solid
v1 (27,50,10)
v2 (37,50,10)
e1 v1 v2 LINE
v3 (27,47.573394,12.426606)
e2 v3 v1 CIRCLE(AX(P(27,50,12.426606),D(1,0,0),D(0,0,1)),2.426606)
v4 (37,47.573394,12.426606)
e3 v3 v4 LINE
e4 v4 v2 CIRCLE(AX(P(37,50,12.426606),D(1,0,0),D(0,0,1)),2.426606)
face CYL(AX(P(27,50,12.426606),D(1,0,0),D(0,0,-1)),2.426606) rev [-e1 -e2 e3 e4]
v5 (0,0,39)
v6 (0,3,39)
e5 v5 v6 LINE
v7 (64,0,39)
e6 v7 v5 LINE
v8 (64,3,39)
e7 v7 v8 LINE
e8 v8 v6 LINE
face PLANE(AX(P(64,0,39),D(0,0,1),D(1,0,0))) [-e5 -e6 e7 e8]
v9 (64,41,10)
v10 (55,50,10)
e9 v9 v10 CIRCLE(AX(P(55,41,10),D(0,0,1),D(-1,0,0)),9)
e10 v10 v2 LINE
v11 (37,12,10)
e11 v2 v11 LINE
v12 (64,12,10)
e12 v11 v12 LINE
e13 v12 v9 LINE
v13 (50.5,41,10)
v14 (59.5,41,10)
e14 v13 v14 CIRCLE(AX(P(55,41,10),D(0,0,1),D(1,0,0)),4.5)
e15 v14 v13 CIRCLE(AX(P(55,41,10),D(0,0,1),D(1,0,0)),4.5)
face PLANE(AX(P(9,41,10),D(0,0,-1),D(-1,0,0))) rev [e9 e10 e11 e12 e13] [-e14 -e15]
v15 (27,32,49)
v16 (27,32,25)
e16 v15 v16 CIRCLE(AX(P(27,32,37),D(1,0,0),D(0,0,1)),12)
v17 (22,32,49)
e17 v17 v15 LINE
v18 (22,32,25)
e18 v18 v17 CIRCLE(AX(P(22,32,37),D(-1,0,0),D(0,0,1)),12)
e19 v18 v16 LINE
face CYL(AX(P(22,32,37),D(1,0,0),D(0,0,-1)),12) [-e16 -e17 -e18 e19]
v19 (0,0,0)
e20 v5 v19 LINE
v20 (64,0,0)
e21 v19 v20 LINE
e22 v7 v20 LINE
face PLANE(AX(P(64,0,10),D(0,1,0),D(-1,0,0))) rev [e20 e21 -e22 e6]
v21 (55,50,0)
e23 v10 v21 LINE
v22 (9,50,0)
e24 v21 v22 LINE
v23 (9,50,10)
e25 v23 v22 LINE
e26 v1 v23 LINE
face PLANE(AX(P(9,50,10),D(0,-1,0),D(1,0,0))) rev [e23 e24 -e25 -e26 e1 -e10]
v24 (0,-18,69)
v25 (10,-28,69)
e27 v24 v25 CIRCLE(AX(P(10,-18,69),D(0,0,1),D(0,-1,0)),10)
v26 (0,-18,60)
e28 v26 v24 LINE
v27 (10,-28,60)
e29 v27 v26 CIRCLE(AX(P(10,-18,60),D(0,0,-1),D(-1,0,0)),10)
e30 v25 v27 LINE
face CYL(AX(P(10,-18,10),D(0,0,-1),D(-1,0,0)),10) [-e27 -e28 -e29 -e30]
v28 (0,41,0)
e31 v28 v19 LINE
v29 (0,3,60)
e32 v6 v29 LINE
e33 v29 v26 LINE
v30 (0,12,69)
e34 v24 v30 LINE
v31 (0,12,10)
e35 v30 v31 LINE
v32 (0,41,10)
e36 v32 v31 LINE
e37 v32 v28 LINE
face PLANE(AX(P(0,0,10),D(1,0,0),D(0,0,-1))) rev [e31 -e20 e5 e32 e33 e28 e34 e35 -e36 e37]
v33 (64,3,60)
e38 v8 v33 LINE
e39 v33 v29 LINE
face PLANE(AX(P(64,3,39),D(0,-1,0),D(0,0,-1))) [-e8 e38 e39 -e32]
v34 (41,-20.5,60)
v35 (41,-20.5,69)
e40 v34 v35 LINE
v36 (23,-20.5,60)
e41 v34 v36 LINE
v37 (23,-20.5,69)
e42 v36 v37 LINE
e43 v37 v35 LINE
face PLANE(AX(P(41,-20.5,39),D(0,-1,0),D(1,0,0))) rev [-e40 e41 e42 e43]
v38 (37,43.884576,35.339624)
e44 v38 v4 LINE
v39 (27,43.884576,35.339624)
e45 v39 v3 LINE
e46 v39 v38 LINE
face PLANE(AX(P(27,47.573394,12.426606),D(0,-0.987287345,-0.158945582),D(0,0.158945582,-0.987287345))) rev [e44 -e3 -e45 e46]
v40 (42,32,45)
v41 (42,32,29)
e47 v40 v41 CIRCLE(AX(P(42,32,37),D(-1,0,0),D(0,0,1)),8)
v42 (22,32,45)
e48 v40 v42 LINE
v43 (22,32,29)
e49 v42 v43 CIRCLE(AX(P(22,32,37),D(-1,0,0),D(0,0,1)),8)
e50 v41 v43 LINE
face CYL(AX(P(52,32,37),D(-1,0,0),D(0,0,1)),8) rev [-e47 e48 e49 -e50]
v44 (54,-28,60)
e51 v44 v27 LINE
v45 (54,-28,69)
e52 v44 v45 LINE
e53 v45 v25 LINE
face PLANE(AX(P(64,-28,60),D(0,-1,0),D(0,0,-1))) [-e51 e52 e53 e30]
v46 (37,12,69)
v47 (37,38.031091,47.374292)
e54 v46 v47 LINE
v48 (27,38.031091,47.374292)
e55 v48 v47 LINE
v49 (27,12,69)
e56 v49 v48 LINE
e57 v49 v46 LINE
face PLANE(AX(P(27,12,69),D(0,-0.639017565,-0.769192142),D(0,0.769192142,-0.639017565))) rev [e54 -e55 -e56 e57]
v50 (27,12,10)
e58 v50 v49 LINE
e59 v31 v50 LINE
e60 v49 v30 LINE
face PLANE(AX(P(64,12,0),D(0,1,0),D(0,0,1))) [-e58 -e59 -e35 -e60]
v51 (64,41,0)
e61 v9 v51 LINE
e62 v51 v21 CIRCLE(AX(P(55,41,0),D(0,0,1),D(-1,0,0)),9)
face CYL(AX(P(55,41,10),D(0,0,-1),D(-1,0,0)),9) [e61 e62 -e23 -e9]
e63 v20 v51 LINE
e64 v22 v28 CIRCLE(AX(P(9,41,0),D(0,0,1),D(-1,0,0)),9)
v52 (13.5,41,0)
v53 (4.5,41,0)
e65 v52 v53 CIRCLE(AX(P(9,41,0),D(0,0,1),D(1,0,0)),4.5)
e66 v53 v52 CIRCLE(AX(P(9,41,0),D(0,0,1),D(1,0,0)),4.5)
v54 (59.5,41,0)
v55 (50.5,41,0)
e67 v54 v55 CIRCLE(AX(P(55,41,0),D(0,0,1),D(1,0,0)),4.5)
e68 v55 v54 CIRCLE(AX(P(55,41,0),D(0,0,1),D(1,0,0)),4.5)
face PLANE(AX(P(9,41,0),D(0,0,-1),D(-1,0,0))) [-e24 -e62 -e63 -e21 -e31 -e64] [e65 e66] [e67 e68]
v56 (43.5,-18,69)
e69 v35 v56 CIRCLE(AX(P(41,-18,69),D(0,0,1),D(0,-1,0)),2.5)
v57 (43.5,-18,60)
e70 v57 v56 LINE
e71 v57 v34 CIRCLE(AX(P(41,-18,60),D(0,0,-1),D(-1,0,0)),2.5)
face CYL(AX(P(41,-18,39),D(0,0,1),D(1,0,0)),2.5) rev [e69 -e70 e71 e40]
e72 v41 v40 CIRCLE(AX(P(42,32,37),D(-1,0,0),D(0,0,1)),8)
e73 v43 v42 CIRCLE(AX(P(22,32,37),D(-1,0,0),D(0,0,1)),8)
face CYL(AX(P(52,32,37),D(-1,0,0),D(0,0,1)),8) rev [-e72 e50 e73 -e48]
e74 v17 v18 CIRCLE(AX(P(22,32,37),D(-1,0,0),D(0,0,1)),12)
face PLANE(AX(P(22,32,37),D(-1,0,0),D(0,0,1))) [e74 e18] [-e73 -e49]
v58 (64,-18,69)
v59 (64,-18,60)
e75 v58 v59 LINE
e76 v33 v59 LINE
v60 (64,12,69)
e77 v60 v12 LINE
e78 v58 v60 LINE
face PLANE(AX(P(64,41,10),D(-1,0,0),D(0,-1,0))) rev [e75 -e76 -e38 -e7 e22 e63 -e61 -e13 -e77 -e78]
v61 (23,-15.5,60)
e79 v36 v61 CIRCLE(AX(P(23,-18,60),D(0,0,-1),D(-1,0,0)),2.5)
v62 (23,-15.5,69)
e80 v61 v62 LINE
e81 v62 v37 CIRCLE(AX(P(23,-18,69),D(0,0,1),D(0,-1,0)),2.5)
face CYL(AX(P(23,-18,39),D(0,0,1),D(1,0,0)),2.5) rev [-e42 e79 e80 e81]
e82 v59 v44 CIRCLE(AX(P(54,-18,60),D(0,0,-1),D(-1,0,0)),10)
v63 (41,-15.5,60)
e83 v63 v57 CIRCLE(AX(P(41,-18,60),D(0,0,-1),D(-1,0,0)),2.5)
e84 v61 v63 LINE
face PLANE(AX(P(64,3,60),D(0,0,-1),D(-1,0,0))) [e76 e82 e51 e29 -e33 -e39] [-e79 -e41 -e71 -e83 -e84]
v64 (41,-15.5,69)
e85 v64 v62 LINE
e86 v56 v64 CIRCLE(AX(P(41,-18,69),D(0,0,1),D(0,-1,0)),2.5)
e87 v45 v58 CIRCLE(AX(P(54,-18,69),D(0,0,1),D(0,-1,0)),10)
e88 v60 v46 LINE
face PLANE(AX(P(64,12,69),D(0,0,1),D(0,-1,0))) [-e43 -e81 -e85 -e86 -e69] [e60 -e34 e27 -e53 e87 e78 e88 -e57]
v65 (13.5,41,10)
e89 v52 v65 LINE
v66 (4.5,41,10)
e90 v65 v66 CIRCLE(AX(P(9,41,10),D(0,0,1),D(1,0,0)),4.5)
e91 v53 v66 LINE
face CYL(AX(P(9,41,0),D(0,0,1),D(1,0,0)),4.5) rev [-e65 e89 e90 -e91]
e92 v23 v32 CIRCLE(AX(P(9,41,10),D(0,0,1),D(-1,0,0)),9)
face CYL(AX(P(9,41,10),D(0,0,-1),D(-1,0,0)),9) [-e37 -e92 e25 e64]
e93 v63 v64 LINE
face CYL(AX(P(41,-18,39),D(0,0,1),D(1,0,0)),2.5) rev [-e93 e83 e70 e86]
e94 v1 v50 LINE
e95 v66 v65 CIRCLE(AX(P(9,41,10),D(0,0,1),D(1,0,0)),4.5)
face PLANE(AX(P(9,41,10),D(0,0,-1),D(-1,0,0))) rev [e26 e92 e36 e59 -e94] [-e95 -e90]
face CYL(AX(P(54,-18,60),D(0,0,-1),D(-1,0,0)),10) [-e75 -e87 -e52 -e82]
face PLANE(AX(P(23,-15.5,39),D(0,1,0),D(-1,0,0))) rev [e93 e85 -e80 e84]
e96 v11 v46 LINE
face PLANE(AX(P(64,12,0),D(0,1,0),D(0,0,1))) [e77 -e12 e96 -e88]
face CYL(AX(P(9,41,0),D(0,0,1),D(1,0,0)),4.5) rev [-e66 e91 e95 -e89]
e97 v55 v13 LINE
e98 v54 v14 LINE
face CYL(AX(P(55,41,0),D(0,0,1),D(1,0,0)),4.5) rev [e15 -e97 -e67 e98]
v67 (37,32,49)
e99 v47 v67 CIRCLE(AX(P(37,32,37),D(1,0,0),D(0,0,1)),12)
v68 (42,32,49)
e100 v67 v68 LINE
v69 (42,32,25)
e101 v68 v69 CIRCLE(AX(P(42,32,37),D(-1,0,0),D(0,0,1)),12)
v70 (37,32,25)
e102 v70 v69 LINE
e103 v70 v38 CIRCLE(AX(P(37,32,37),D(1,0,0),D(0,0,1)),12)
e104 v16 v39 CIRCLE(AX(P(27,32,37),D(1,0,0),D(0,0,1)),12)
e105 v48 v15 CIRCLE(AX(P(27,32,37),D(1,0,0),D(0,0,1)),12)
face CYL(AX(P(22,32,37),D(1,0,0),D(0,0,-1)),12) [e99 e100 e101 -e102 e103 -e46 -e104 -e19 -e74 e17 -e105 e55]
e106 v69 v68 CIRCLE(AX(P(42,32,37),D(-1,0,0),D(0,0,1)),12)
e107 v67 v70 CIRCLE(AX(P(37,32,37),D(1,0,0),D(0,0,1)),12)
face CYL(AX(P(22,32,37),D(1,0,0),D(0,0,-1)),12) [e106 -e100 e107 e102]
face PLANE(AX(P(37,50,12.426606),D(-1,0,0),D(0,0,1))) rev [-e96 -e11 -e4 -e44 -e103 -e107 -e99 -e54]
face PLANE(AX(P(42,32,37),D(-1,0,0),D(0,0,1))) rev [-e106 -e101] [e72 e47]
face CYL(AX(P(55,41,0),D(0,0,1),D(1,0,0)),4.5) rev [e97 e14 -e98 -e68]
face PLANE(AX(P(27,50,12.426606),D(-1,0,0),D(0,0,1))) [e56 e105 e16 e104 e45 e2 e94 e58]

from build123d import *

# Parameters (mm, degrees)
BACK_PLATE_DEPTH        = 10
MOUNTING_HOLES_SKETCH_R = 4.5
MOUNTING_HOLES_2X_DEPTH = 10
L_BASE_BODY_DEPTH       = 64
HUB_BOSS_SKETCH_R       = 12
HUB_BOSS_DEPTH          = 10
SUPPORT_RIB_DEPTH       = 5
HUB_BORE_SKETCH_R       = 8
HUB_BORE_16_DEPTH       = 30
FRONT_SLOT_DEPTH        = 30
EDGE_FILLET_R10_A_R     = 10
EDGE_FILLET_R10_B_R     = 10


with BuildPart() as part:
    # Back Plate Sketch → Back Plate (new body)
    with BuildSketch(Plane.XY):
        with BuildLine():
            Line((0, 0), (0, 41))
            ThreePointArc((0, 41), (2.636038969, 47.363961031), (9, 50))
            Line((9, 50), (55, 50))
            ThreePointArc((55, 50), (61.363961031, 47.363961031), (64, 41))
            Line((64, 41), (64, 0))
            Line((64, 0), (0, 0))
        make_face()
    extrude(amount=BACK_PLATE_DEPTH)

    # Mounting Holes Sketch → Mounting Holes 2x (cut)
    with BuildSketch(Plane.XY.offset(10)):
        with Locations((9, 41)):
            Circle(MOUNTING_HOLES_SKETCH_R)
        with Locations((55, 41)):
            Circle(MOUNTING_HOLES_SKETCH_R)
    extrude(amount=-MOUNTING_HOLES_2X_DEPTH, mode=Mode.SUBTRACT)

    # L-Base Profile Sketch → L-Base Body (add)
    with BuildSketch(Plane.ZY):
        Polygon((0, 0), (39, 0), (39, 3), (60, 3), (60, -28), (69, -28), (69, 12), (0, 12), align=None)
    extrude(amount=-L_BASE_BODY_DEPTH)



with BuildPart() as body_2:
    # Hub Boss Sketch → Hub Boss (new, symmetric)
    with BuildSketch(Plane.ZY.offset(-32)):
        with Locations((37, 32)):
            Circle(HUB_BOSS_SKETCH_R)
    extrude(amount=HUB_BOSS_DEPTH, both=True)


with BuildPart() as part_1:
    add(part.part)

    add(body_2.part)  # Support Rib merges body 2
    # Support Rib Sketch → Support Rib (add, symmetric)
    with BuildSketch(Plane.ZY.offset(-32)):
        with BuildLine():
            Line((10, 12), (69, 12))
            Line((69, 12), (44.830635443, 41.092917494))
            Line((44.830635443, 41.092917494), (35.339623776, 43.884576172))
            Line((35.339623776, 43.884576172), (12.426606273, 47.573393727))
            ThreePointArc((12.426606273, 47.573393727), (10.710736522, 48.284130249), (10, 50))
            Line((10, 50), (10, 12))
        make_face()
    extrude(amount=SUPPORT_RIB_DEPTH, both=True)

    # Hub Bore Sketch → Hub Bore Ø16 (cut, symmetric)
    with BuildSketch(Plane.ZY.offset(-22)):
        with Locations((37, 32)):
            Circle(HUB_BORE_SKETCH_R)
    extrude(amount=HUB_BORE_16_DEPTH, both=True, mode=Mode.SUBTRACT)

    # Front Slot Sketch → Front Slot (cut, symmetric)
    with BuildSketch(Plane.XY.offset(69)):
        with BuildLine():
            Line((23, -15.5), (41, -15.5))
            ThreePointArc((41, -15.5), (43.5, -18), (41, -20.5))
            Line((41, -20.5), (23, -20.5))
            ThreePointArc((23, -20.5), (20.5, -18), (23, -15.5))
        make_face()
    extrude(amount=FRONT_SLOT_DEPTH, both=True, mode=Mode.SUBTRACT)

    # Edge Fillet R10 A
    edge_fillet_r10_a_edges = [part_1.edges().sort_by_distance(p)[0] for p in [
        (0, -28, 64.5),
    ]]
    fillet(edge_fillet_r10_a_edges, radius=EDGE_FILLET_R10_A_R)

    # Edge Fillet R10 B
    edge_fillet_r10_b_edges = [part_1.edges().sort_by_distance(p)[0] for p in [
        (64, -28, 64.5),
    ]]
    fillet(edge_fillet_r10_b_edges, radius=EDGE_FILLET_R10_B_R)


solid = part_1.part
